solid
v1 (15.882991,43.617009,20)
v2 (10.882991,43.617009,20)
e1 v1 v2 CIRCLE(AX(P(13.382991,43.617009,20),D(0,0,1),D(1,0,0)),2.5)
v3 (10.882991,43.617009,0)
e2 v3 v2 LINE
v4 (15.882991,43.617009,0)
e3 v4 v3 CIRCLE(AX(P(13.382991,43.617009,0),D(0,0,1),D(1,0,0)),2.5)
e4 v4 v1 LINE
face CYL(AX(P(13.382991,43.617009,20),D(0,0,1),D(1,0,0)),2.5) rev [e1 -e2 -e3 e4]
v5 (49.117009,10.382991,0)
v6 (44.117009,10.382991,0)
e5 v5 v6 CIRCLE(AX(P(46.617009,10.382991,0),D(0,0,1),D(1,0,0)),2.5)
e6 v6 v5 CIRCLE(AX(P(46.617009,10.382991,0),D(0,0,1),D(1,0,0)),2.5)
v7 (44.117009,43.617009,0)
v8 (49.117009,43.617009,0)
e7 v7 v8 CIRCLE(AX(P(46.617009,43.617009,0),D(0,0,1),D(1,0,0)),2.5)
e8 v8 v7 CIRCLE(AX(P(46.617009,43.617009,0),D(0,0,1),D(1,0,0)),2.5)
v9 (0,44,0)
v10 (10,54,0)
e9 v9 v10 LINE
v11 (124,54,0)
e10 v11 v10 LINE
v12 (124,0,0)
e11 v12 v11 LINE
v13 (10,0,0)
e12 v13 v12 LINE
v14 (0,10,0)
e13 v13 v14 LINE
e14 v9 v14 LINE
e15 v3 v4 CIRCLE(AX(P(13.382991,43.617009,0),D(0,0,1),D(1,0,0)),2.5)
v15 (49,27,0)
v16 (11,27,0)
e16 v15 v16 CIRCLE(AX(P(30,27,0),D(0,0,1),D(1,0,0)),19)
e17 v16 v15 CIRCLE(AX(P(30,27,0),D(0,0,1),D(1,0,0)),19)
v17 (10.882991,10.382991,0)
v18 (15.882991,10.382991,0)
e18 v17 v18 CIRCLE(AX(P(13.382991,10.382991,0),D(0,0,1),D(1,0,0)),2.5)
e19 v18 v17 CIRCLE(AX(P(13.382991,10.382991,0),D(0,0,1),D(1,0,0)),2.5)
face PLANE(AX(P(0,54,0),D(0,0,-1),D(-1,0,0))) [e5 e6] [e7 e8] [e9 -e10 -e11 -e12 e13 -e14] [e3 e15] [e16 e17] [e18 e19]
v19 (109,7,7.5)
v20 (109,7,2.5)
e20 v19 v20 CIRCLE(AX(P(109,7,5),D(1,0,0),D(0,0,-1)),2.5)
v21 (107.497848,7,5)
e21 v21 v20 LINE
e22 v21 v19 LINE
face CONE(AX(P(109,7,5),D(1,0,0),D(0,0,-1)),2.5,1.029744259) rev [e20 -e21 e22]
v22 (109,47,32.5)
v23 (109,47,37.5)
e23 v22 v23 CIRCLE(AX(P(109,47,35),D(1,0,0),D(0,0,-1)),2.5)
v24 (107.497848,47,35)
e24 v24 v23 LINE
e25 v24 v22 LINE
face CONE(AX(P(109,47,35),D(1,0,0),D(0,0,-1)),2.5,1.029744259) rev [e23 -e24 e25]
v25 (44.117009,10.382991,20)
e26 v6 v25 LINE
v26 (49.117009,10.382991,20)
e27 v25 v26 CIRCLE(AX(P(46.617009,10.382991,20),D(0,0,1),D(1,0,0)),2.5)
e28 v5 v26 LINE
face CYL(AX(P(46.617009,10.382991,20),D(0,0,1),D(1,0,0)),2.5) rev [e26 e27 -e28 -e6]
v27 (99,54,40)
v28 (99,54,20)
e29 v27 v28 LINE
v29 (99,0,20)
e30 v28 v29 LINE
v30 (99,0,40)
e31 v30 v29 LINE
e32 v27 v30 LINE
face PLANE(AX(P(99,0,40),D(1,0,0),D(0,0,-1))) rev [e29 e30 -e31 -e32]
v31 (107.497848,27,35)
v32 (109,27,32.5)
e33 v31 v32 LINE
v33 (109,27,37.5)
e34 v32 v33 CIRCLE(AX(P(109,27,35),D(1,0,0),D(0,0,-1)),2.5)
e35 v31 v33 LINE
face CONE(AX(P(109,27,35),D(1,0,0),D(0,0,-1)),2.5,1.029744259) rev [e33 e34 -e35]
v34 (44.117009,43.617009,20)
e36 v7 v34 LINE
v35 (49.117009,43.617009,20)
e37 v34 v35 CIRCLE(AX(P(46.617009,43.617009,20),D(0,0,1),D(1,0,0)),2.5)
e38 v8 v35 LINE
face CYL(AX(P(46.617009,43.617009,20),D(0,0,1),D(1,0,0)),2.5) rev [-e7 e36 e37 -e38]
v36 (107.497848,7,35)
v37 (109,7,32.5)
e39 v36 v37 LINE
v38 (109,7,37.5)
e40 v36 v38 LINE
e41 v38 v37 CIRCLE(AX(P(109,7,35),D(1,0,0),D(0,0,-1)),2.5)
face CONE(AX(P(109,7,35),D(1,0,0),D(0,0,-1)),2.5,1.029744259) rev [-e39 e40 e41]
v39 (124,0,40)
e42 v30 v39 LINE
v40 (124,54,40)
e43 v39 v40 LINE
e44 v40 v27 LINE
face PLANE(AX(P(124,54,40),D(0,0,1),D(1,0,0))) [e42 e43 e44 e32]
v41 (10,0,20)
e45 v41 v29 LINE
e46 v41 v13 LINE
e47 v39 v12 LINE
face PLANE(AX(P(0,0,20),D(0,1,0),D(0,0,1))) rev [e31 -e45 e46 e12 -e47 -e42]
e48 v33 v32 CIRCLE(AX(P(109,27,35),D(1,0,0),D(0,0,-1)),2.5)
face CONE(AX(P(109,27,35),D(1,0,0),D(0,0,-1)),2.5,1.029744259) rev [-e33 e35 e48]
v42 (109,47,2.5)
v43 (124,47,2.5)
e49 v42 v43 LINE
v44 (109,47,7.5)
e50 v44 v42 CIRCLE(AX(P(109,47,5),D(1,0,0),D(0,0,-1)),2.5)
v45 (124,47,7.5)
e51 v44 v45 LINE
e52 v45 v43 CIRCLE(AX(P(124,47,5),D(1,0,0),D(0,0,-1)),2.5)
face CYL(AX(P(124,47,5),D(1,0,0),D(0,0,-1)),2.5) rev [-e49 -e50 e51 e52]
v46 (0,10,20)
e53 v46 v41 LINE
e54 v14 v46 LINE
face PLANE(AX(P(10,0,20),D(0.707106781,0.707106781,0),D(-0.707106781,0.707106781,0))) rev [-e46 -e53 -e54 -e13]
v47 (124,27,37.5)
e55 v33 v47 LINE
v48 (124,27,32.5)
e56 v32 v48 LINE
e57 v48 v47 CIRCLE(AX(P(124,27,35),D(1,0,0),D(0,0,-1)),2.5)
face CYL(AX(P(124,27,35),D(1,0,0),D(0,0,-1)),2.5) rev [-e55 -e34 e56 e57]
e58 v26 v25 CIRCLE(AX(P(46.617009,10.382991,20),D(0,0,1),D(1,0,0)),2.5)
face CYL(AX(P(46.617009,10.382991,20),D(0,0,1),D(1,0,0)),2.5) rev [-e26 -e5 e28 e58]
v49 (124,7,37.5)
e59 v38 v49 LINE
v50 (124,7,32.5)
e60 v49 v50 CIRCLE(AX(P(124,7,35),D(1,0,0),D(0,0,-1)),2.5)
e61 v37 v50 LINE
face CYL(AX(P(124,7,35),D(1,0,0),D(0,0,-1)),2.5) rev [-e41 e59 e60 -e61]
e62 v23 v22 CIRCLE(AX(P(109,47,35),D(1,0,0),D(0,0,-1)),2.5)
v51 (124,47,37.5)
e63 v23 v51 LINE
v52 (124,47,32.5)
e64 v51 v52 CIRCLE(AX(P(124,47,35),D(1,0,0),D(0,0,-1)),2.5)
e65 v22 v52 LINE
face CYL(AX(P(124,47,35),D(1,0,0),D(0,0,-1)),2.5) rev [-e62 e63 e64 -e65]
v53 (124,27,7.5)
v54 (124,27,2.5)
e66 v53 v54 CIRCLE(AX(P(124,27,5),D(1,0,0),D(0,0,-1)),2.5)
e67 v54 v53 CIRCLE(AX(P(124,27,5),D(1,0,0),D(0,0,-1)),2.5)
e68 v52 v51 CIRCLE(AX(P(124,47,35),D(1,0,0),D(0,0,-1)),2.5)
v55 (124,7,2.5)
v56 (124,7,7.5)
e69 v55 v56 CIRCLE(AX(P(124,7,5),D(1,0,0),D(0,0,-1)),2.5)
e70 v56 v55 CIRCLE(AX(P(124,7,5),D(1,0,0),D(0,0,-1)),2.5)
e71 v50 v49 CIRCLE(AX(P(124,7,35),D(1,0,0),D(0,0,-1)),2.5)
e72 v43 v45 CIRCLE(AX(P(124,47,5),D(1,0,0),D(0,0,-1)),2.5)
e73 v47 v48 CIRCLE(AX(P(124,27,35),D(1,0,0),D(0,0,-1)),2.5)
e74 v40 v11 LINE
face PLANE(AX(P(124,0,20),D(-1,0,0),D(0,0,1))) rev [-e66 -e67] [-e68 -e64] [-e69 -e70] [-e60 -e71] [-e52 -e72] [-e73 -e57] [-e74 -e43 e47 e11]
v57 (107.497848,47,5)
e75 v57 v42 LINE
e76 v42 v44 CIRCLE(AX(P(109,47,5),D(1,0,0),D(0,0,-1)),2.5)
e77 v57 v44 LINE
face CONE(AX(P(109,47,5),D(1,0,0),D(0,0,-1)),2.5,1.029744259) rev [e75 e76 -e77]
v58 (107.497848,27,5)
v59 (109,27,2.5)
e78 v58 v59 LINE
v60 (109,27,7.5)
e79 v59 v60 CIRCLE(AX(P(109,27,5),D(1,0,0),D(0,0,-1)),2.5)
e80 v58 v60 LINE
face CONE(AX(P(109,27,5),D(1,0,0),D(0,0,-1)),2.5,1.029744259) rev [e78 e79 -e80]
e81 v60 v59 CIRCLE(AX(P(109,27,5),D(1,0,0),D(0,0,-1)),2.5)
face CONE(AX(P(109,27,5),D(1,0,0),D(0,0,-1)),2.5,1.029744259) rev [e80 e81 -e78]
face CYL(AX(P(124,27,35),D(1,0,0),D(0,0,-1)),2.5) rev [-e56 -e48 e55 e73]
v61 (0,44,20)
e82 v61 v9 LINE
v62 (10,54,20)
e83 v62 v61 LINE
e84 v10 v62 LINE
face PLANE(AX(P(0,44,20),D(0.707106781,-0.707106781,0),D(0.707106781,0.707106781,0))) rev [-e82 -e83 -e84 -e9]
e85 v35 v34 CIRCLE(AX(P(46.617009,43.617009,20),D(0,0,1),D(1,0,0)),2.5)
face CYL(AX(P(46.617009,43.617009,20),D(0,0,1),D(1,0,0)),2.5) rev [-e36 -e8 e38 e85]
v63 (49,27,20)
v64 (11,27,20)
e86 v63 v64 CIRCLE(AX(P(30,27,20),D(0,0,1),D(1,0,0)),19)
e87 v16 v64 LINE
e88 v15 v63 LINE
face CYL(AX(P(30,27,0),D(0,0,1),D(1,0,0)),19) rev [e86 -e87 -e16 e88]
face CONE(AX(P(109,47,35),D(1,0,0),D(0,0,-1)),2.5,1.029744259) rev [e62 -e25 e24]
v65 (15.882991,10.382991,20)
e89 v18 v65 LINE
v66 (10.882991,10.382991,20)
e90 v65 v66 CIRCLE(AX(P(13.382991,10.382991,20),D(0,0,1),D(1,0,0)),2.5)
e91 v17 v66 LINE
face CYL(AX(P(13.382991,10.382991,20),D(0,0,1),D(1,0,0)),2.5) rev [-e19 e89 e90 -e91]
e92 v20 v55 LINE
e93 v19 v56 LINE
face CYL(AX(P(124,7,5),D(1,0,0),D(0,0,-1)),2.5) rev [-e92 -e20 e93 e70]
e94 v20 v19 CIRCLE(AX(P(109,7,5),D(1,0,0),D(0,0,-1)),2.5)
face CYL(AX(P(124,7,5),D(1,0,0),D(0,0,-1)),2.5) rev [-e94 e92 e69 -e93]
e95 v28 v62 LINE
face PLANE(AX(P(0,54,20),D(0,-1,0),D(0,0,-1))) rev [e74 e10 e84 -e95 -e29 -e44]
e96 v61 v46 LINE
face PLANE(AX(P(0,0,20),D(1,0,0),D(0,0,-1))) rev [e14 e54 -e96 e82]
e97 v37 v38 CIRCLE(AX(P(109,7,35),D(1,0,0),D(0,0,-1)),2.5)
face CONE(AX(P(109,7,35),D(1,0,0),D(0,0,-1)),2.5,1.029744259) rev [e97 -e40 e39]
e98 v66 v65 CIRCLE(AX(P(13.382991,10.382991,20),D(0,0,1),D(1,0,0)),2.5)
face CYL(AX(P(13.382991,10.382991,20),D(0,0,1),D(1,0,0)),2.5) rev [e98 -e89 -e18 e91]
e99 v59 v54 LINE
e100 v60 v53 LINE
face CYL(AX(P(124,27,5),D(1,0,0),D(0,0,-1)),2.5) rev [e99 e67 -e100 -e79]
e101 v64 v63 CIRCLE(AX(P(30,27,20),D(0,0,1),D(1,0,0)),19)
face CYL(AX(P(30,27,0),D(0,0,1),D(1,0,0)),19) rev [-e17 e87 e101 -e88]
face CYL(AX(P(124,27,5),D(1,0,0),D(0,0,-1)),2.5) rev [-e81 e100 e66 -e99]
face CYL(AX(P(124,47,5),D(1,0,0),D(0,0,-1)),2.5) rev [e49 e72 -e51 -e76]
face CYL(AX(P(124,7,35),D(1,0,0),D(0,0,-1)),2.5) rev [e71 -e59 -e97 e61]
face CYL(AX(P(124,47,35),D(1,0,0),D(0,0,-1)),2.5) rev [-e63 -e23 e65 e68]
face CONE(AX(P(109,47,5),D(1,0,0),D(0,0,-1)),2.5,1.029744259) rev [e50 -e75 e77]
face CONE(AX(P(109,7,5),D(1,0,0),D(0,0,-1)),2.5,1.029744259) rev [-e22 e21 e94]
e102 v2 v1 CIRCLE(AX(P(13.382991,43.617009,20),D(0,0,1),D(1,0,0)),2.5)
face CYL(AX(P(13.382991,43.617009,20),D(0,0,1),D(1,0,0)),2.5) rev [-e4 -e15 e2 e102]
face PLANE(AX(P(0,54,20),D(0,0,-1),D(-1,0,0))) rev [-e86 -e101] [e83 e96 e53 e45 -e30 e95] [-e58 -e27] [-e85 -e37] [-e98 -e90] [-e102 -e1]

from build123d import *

# Parameters (mm, degrees)
SKETCH1_W             = 124
SKETCH1_H             = 54
BOSS_EXTRUDE1_DEPTH   = 20
CHAMFER1_SIZE         = 10
SKETCH2_R             = 19
CUT_EXTRUDE1_DEPTH    = 20
M6_TAPPED_HOLE1_D     = 5
CIRPATTERN1_COUNT     = 4
SKETCH7_W             = 25
SKETCH7_H             = 54
BOSS_EXTRUDE2_DEPTH   = 20
M6_TAPPED_HOLE2_D     = 5
M6_TAPPED_HOLE2_DEPTH = 15
M6_TAPPED_HOLE2_TIP   = 1.502151548


with BuildPart() as part:
    # Sketch1 → Boss-Extrude1 (new body)
    with BuildSketch(Plane.XY):
        with Locations((62, 27)):
            Rectangle(SKETCH1_W, SKETCH1_H)
    extrude(amount=BOSS_EXTRUDE1_DEPTH)

    # Chamfer1
    chamfer1_edges = [part.edges().sort_by_distance(p)[0] for p in [
        (0, 54, 10),
        (0, 0, 10),
    ]]
    chamfer(chamfer1_edges, length=CHAMFER1_SIZE)

    # Sketch2 → Cut-Extrude1 (cut)
    with BuildSketch(Plane.XY.offset(20)):
        with Locations((30, 27)):
            Circle(SKETCH2_R)
    extrude(amount=-CUT_EXTRUDE1_DEPTH, mode=Mode.SUBTRACT)

    # M6 Tapped Hole1 (through all)
    with Locations(Plane.XY.offset(20)):
        with Locations((46.617009358, 43.617009358)):
            m6_tapped_hole1 = Hole(M6_TAPPED_HOLE1_D / 2)

    # CirPattern1: M6 Tapped Hole1 ×4 about axis
    cirpattern1_axis = Axis((30, 27, 0), (0, 0, 1))
    for i in range(1, CIRPATTERN1_COUNT):
        add(m6_tapped_hole1.rotate(cirpattern1_axis, i * 360 / CIRPATTERN1_COUNT), mode=Mode.SUBTRACT)

    # Sketch7 → Boss-Extrude2 (add)
    with BuildSketch(Plane.XY.offset(20)):
        with Locations((111.5, 27)):
            Rectangle(SKETCH7_W, SKETCH7_H)
    extrude(amount=BOSS_EXTRUDE2_DEPTH)

    # M6 Tapped Hole2
    with Locations(Plane(origin=(124, 0, 0), x_dir=(0, 0, -1), z_dir=(1, 0, 0))):
        with Locations((-35, 47), (-5, 47), (-35, 7), (-5, 7), (-35, 27), (-5, 27)):
            Hole(M6_TAPPED_HOLE2_D / 2, depth=M6_TAPPED_HOLE2_DEPTH)
            with Locations((0, 0, -(M6_TAPPED_HOLE2_DEPTH + M6_TAPPED_HOLE2_TIP / 2))):  # 118° drill point
                Cone(0, M6_TAPPED_HOLE2_D / 2, M6_TAPPED_HOLE2_TIP, mode=Mode.SUBTRACT)


solid = part.part
